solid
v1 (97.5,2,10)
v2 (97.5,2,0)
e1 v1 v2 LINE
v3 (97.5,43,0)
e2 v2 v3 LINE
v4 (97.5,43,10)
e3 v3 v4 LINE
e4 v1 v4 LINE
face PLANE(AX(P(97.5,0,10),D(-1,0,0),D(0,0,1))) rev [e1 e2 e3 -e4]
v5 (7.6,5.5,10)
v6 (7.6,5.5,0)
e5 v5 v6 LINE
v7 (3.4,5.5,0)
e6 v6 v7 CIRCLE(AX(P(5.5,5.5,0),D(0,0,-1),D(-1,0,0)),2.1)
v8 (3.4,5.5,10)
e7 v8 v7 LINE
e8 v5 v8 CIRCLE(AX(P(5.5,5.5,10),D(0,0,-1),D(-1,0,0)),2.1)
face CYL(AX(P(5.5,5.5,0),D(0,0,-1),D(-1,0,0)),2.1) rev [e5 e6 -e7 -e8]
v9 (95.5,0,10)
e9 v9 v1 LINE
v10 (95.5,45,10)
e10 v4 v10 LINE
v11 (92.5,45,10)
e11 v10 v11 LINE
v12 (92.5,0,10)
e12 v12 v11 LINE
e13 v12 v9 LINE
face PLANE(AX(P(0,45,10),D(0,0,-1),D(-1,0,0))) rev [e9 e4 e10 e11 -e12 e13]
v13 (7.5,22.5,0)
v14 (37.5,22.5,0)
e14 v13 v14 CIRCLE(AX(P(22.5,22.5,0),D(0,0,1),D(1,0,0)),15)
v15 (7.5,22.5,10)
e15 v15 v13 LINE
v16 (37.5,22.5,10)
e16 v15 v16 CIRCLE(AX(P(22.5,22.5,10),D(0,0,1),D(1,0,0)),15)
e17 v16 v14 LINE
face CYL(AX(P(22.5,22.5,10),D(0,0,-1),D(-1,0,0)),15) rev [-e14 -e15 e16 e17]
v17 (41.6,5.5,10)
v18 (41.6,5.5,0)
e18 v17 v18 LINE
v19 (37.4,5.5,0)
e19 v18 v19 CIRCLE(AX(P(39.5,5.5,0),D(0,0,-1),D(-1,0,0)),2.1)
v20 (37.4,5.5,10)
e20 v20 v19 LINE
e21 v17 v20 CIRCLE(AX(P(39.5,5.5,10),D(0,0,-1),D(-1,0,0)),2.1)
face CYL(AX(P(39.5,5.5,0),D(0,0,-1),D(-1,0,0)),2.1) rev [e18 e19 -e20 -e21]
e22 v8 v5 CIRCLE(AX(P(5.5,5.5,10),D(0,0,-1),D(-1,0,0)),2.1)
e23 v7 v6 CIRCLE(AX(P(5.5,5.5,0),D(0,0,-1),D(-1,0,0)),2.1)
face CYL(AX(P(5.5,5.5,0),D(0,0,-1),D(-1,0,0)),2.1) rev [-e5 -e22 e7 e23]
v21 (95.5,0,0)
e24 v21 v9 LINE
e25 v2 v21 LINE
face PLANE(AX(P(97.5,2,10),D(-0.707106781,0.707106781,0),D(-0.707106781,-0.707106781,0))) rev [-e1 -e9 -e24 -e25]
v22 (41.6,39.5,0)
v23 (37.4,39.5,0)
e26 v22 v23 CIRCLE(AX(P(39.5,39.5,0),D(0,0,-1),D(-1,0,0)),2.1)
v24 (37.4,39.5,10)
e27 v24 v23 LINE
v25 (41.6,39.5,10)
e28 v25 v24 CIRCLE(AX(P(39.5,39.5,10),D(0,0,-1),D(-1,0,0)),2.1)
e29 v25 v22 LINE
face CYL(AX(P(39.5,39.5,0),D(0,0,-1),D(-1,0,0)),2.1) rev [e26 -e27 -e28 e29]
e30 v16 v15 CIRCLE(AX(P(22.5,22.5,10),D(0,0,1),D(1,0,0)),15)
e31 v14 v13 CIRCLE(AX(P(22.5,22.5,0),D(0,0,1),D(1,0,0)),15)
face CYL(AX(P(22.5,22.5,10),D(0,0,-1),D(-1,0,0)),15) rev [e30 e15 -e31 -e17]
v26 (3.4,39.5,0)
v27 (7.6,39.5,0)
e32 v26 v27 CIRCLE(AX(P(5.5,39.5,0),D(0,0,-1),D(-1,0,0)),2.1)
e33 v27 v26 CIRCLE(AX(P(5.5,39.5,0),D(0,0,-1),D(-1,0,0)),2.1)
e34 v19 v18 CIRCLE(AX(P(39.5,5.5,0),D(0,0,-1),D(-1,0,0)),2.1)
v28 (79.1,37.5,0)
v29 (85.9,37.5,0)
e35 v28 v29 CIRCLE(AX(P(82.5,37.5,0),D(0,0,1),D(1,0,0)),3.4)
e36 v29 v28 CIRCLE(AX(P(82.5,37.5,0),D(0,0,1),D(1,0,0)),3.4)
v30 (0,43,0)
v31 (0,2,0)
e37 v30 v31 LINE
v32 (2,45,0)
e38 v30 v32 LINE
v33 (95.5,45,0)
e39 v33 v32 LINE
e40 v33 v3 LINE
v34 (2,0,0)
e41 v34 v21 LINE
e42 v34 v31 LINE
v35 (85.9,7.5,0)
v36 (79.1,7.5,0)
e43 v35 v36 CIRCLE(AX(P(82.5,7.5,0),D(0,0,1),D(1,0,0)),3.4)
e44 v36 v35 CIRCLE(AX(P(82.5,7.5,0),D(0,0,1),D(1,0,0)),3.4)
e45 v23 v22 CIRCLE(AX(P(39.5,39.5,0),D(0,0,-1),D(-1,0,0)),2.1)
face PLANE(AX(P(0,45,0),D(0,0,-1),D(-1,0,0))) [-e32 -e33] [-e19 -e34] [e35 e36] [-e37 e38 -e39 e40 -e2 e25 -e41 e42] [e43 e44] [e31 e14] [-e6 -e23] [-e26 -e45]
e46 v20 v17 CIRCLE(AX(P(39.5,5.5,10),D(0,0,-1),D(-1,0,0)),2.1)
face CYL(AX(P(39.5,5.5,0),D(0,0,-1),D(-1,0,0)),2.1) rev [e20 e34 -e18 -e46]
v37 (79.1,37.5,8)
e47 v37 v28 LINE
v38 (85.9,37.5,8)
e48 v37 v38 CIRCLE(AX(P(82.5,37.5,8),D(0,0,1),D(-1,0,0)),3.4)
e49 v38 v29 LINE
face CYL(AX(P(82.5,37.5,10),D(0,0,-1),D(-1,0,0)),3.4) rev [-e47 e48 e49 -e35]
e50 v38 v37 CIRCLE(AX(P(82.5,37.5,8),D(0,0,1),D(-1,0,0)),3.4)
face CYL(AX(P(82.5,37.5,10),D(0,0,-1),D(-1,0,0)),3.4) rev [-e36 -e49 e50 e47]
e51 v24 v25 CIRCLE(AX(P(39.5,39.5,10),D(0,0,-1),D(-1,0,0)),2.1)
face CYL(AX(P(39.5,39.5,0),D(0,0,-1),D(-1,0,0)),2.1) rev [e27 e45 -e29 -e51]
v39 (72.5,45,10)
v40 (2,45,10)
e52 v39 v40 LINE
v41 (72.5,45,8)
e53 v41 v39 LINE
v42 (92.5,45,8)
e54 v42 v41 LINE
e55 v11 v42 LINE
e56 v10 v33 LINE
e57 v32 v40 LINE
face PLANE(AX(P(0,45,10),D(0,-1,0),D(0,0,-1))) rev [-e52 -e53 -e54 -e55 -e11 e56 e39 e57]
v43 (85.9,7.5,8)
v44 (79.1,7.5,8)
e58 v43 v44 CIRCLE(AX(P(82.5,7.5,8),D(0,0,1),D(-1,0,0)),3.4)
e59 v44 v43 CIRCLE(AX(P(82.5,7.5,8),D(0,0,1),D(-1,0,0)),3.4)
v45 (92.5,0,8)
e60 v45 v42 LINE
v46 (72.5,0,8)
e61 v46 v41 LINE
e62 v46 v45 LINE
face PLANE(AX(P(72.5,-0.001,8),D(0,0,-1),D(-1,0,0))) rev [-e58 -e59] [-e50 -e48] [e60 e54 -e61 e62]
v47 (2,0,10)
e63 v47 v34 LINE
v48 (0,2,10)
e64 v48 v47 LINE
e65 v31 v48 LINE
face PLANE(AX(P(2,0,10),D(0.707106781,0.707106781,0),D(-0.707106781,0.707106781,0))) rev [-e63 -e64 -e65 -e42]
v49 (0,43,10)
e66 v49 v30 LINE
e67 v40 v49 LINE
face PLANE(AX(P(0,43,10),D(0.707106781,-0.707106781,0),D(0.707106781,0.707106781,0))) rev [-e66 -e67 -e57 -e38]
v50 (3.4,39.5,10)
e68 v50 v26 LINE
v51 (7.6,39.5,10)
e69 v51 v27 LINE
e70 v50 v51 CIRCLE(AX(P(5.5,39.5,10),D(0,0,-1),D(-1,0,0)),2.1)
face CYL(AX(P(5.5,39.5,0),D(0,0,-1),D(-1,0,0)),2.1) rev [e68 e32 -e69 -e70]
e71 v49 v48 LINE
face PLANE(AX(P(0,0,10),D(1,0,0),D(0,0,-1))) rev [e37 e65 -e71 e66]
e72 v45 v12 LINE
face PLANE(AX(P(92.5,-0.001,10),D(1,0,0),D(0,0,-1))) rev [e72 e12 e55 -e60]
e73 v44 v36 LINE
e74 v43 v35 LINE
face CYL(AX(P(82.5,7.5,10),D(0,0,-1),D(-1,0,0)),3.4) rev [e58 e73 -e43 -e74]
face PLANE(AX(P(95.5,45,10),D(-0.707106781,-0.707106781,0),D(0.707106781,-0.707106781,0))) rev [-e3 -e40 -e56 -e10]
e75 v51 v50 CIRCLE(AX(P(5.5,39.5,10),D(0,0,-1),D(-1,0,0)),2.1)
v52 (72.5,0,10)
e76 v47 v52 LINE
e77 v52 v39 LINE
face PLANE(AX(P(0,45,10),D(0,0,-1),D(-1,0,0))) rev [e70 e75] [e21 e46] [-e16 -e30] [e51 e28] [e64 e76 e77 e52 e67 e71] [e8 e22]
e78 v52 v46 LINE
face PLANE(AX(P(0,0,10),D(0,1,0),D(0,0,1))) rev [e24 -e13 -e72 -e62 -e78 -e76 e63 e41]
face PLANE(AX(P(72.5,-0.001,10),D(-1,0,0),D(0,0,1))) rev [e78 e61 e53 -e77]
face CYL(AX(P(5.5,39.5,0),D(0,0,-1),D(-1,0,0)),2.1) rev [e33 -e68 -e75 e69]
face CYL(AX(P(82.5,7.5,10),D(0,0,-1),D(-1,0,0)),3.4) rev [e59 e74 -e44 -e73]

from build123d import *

# Parameters (mm, degrees)
SKETCH1_W             = 97.5
SKETCH1_H             = 45
SKETCH1_R             = 15
SKETCH1_R_2           = 3.4
BOSS_EXTRUDE1_DEPTH   = 10
CUT_EXTRUDE1_REACH    = 109.848
SKETCH2_W             = 20
SKETCH2_H             = 2
M5_TAPPED_HOLE1_D     = 4.2
M5_TAPPED_HOLE1_DEPTH = 12.4
M5_TAPPED_HOLE1_TIP   = 1.2618073
CHAMFER1_SIZE         = 2


with BuildPart() as part:
    # Sketch1 → Boss-Extrude1 (new body)
    with BuildSketch(Plane.XY):
        with Locations((48.75, 22.5)):
            Rectangle(SKETCH1_W, SKETCH1_H)
        with Locations((22.5, 22.5)):
            Circle(SKETCH1_R, mode=Mode.SUBTRACT)
        with Locations((82.5, 37.5)):
            Circle(SKETCH1_R_2, mode=Mode.SUBTRACT)
        with Locations((82.5, 7.5)):
            Circle(SKETCH1_R_2, mode=Mode.SUBTRACT)
    extrude(amount=BOSS_EXTRUDE1_DEPTH)

    # Sketch2 → Cut-Extrude1 (cut, up to next)
    with BuildSketch(Plane(origin=(0, 45, 0), x_dir=(1, 0, 0), z_dir=(0, 1, 0)), mode=Mode.PRIVATE) as cut_extrude1_sk1:
        with Locations((82.5, -9)):
            Rectangle(SKETCH2_W, SKETCH2_H)
    cut_extrude1_tool1 = extrude(cut_extrude1_sk1.sketch, amount=-CUT_EXTRUDE1_REACH, mode=Mode.PRIVATE) & part.part
    add(cut_extrude1_tool1.solids().sort_by_distance((82.5, 45, 9))[0], mode=Mode.SUBTRACT)

    # M5 Tapped Hole1
    with Locations(Plane(origin=(0, 0, 0), x_dir=(-1, 0, 0), z_dir=(0, 0, -1))):
        with Locations((-39.5, 5.5), (-5.5, 5.5), (-5.5, 39.5), (-39.5, 39.5)):
            Hole(M5_TAPPED_HOLE1_D / 2, depth=M5_TAPPED_HOLE1_DEPTH)
            with Locations((0, 0, -(M5_TAPPED_HOLE1_DEPTH + M5_TAPPED_HOLE1_TIP / 2))):  # 118° drill point
                Cone(0, M5_TAPPED_HOLE1_D / 2, M5_TAPPED_HOLE1_TIP, mode=Mode.SUBTRACT)

    # Chamfer1
    chamfer1_edges = [part.edges().sort_by_distance(p)[0] for p in [
        (0, 45, 5),
        (97.5, 45, 5),
        (97.5, 0, 5),
        (0, 0, 5),
    ]]
    chamfer(chamfer1_edges, length=CHAMFER1_SIZE)


solid = part.part
